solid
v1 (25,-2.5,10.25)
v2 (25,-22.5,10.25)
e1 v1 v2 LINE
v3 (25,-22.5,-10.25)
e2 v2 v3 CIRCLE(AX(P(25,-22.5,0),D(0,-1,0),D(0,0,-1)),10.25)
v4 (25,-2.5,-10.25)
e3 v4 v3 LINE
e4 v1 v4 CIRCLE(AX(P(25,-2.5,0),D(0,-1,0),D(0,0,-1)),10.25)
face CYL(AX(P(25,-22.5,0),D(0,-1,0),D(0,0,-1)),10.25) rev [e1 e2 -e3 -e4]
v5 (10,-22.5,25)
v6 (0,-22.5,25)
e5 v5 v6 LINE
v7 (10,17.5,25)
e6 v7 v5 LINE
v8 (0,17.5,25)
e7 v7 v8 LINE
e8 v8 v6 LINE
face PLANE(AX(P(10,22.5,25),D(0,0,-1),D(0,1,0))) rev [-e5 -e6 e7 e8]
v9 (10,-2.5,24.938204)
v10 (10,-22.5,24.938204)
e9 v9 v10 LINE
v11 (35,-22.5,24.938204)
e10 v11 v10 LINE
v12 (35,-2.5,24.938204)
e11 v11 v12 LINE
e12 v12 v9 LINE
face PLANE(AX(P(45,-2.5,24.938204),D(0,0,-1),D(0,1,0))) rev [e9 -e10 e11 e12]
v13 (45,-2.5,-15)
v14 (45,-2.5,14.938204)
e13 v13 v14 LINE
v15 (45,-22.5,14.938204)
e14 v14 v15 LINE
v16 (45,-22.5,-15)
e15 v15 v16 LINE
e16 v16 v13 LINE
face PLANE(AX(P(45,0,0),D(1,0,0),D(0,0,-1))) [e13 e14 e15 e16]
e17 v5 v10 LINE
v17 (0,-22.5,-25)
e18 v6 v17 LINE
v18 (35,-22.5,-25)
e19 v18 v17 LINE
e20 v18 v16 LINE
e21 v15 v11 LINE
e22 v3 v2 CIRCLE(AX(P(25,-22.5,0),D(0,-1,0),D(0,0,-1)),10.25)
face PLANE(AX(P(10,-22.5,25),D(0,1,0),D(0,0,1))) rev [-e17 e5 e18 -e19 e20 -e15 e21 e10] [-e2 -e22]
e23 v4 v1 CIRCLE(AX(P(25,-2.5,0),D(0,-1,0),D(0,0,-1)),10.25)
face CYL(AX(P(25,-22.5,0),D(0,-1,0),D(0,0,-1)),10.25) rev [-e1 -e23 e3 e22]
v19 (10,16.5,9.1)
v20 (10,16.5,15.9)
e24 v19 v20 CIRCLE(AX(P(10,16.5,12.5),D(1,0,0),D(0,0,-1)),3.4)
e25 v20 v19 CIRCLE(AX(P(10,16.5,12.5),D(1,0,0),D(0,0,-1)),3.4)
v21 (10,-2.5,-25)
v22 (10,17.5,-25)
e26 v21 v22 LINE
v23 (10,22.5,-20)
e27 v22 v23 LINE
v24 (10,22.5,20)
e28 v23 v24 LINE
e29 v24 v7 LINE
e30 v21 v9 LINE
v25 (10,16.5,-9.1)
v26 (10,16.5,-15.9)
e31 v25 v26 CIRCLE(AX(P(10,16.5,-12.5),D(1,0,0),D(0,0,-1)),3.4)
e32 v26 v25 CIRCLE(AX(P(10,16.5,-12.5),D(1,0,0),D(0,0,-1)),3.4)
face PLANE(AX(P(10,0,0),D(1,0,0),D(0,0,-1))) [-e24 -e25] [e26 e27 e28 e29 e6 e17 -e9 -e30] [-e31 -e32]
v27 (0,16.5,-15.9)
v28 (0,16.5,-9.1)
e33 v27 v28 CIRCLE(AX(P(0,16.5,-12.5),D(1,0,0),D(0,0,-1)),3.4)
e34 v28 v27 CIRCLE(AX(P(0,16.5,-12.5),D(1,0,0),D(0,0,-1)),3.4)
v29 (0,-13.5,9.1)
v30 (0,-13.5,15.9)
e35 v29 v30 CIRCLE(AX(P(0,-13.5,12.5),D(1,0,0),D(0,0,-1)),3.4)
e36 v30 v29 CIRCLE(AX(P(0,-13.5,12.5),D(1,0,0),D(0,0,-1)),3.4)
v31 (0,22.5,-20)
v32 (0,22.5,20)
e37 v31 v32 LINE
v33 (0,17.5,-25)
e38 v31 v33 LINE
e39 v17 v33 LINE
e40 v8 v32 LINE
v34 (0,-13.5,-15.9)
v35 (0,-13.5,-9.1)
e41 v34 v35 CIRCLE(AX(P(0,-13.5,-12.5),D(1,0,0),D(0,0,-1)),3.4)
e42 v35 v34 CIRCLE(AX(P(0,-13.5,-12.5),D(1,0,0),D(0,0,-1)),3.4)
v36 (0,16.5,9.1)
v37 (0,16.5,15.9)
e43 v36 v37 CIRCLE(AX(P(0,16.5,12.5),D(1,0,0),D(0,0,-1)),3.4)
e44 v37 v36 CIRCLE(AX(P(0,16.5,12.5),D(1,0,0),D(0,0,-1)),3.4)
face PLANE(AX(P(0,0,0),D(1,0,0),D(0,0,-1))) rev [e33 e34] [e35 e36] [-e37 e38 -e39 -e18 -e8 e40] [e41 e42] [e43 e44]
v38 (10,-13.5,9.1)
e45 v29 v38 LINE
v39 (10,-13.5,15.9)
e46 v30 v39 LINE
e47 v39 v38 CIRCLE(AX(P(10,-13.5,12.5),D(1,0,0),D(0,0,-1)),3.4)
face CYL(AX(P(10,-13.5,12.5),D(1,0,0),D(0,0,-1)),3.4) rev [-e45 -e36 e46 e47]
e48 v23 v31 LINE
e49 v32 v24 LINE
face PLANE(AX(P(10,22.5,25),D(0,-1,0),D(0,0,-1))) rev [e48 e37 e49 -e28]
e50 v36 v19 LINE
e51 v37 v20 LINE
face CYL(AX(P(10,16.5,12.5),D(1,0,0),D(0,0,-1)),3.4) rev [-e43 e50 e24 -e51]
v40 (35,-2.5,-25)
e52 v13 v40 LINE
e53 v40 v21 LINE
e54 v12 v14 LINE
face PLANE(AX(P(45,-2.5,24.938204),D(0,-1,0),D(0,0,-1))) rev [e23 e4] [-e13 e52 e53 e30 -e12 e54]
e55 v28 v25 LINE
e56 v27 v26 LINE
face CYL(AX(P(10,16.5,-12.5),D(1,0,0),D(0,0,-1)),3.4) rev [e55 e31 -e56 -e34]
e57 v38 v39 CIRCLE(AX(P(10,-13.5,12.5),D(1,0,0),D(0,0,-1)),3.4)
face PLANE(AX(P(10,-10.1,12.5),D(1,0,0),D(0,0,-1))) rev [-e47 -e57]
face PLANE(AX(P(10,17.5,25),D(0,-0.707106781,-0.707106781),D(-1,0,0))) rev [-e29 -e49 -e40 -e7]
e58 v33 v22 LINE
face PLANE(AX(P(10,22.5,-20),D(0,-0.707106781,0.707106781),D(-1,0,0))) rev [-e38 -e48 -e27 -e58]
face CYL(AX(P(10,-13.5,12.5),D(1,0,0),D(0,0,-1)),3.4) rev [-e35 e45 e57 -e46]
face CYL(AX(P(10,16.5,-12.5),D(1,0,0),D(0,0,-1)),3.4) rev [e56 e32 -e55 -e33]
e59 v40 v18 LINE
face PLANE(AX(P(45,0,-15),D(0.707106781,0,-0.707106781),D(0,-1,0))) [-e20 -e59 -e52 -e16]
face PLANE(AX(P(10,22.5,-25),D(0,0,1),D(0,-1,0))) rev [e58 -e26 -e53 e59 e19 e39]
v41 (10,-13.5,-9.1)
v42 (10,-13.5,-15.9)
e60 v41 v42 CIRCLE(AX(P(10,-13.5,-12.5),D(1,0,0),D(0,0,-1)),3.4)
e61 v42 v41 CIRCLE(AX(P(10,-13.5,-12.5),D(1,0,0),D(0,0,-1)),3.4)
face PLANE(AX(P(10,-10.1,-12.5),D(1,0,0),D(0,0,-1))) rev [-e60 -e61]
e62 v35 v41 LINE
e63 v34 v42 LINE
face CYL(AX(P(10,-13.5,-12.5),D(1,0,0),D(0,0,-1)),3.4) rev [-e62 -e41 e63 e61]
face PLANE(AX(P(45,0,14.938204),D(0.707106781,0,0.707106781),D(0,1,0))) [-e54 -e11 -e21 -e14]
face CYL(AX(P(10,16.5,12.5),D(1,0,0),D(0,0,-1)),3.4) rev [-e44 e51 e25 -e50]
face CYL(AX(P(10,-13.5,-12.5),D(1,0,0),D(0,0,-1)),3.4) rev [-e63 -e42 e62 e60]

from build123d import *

# Parameters (mm, degrees)
SKETCH_1_W                  = 50
SKETCH_1_H                  = 45
EXTRUDE_1_DEPTH             = 10
SKETCH_2_W                  = 49.938204031
SKETCH_2_H                  = 20
EXTRUDE_2_DEPTH             = 35
HOLE_WIZARD_20_5_20_5_1_D   = 20.5
SKETCH_6_W                  = 3.4
SKETCH_6_H                  = 10
HOLE_WIZARD_M8_1_AT_2_COUNT = 2
HOLE_WIZARD_M8_1_AT_2_PITCH = 25
HOLE_WIZARD_M8_1_AT_3_COUNT = 2
HOLE_WIZARD_M8_1_AT_3_PITCH = 30
HOLE_WIZARD_M8_1_AT_4_COUNT = 2
HOLE_WIZARD_M8_1_AT_4_PITCH = 39.05124838
CHAMFER_1_SIZE              = 10
CHAMFER_2_SIZE              = 5


with BuildPart() as part:
    # 草图1 → 凸台-拉伸1 (new body)
    with BuildSketch(Plane(origin=(0, 0, 0), x_dir=(0, 0, -1), z_dir=(1, 0, 0))):
        Rectangle(SKETCH_1_W, SKETCH_1_H)
    extrude(amount=EXTRUDE_1_DEPTH)

    # 草图2 → 凸台-拉伸2 (add)
    with BuildSketch(Plane(origin=(10, 0, 0), x_dir=(0, 0, -1), z_dir=(1, 0, 0))):
        with Locations((0.030897984, -12.5)):
            Rectangle(SKETCH_2_W, SKETCH_2_H)
    extrude(amount=EXTRUDE_2_DEPTH)

    # Ø20.5 (20.5) 直径孔1 (through all)
    with Locations(Plane(origin=(0, -22.5, 0), x_dir=(-1, 0, 0), z_dir=(0, -1, 0))):
        with Locations((-25, 0)):
            Hole(HOLE_WIZARD_20_5_20_5_1_D / 2)

    # 草图6 → M8 螺纹孔1 (revolve, cut)
    with BuildSketch(Plane(origin=(10, 16.5, 12.5), x_dir=(0, 0, -1), z_dir=(0, 1, 0))):
        with Locations((1.7, 5)):
            Rectangle(SKETCH_6_W, SKETCH_6_H)
    hole_wizard_m8_1 = revolve(axis=Axis((16.35, 16.5, 12.5), (-1, 0, 0)), mode=Mode.SUBTRACT)

    # M8 螺纹孔1 at 2: M8 螺纹孔1 ×2
    with Locations(*[(0, 0, -i * HOLE_WIZARD_M8_1_AT_2_PITCH) for i in range(1, HOLE_WIZARD_M8_1_AT_2_COUNT)]):
        add(hole_wizard_m8_1, mode=Mode.SUBTRACT)

    # M8 螺纹孔1 at 3: M8 螺纹孔1 ×2
    with Locations(*[(0, -i * HOLE_WIZARD_M8_1_AT_3_PITCH, 0) for i in range(1, HOLE_WIZARD_M8_1_AT_3_COUNT)]):
        add(hole_wizard_m8_1, mode=Mode.SUBTRACT)

    # M8 螺纹孔1 at 4: M8 螺纹孔1 ×2
    with Locations(*[Vector(0, -0.7682212795973759, -0.64018439966448) * (i * HOLE_WIZARD_M8_1_AT_4_PITCH) for i in range(1, HOLE_WIZARD_M8_1_AT_4_COUNT)]):
        add(hole_wizard_m8_1, mode=Mode.SUBTRACT)

    # 倒角1
    chamfer_1_edges = [part.edges().sort_by_distance(p)[0] for p in [
        (45, -12.5, -25),
        (45, -12.5, 24.938204031),
    ]]
    chamfer(chamfer_1_edges, length=CHAMFER_1_SIZE)

    # 倒角2
    chamfer_2_edges = [part.edges().sort_by_distance(p)[0] for p in [
        (5, 22.5, 25),
        (5, 22.5, -25),
    ]]
    chamfer(chamfer_2_edges, length=CHAMFER_2_SIZE)


solid = part.part
